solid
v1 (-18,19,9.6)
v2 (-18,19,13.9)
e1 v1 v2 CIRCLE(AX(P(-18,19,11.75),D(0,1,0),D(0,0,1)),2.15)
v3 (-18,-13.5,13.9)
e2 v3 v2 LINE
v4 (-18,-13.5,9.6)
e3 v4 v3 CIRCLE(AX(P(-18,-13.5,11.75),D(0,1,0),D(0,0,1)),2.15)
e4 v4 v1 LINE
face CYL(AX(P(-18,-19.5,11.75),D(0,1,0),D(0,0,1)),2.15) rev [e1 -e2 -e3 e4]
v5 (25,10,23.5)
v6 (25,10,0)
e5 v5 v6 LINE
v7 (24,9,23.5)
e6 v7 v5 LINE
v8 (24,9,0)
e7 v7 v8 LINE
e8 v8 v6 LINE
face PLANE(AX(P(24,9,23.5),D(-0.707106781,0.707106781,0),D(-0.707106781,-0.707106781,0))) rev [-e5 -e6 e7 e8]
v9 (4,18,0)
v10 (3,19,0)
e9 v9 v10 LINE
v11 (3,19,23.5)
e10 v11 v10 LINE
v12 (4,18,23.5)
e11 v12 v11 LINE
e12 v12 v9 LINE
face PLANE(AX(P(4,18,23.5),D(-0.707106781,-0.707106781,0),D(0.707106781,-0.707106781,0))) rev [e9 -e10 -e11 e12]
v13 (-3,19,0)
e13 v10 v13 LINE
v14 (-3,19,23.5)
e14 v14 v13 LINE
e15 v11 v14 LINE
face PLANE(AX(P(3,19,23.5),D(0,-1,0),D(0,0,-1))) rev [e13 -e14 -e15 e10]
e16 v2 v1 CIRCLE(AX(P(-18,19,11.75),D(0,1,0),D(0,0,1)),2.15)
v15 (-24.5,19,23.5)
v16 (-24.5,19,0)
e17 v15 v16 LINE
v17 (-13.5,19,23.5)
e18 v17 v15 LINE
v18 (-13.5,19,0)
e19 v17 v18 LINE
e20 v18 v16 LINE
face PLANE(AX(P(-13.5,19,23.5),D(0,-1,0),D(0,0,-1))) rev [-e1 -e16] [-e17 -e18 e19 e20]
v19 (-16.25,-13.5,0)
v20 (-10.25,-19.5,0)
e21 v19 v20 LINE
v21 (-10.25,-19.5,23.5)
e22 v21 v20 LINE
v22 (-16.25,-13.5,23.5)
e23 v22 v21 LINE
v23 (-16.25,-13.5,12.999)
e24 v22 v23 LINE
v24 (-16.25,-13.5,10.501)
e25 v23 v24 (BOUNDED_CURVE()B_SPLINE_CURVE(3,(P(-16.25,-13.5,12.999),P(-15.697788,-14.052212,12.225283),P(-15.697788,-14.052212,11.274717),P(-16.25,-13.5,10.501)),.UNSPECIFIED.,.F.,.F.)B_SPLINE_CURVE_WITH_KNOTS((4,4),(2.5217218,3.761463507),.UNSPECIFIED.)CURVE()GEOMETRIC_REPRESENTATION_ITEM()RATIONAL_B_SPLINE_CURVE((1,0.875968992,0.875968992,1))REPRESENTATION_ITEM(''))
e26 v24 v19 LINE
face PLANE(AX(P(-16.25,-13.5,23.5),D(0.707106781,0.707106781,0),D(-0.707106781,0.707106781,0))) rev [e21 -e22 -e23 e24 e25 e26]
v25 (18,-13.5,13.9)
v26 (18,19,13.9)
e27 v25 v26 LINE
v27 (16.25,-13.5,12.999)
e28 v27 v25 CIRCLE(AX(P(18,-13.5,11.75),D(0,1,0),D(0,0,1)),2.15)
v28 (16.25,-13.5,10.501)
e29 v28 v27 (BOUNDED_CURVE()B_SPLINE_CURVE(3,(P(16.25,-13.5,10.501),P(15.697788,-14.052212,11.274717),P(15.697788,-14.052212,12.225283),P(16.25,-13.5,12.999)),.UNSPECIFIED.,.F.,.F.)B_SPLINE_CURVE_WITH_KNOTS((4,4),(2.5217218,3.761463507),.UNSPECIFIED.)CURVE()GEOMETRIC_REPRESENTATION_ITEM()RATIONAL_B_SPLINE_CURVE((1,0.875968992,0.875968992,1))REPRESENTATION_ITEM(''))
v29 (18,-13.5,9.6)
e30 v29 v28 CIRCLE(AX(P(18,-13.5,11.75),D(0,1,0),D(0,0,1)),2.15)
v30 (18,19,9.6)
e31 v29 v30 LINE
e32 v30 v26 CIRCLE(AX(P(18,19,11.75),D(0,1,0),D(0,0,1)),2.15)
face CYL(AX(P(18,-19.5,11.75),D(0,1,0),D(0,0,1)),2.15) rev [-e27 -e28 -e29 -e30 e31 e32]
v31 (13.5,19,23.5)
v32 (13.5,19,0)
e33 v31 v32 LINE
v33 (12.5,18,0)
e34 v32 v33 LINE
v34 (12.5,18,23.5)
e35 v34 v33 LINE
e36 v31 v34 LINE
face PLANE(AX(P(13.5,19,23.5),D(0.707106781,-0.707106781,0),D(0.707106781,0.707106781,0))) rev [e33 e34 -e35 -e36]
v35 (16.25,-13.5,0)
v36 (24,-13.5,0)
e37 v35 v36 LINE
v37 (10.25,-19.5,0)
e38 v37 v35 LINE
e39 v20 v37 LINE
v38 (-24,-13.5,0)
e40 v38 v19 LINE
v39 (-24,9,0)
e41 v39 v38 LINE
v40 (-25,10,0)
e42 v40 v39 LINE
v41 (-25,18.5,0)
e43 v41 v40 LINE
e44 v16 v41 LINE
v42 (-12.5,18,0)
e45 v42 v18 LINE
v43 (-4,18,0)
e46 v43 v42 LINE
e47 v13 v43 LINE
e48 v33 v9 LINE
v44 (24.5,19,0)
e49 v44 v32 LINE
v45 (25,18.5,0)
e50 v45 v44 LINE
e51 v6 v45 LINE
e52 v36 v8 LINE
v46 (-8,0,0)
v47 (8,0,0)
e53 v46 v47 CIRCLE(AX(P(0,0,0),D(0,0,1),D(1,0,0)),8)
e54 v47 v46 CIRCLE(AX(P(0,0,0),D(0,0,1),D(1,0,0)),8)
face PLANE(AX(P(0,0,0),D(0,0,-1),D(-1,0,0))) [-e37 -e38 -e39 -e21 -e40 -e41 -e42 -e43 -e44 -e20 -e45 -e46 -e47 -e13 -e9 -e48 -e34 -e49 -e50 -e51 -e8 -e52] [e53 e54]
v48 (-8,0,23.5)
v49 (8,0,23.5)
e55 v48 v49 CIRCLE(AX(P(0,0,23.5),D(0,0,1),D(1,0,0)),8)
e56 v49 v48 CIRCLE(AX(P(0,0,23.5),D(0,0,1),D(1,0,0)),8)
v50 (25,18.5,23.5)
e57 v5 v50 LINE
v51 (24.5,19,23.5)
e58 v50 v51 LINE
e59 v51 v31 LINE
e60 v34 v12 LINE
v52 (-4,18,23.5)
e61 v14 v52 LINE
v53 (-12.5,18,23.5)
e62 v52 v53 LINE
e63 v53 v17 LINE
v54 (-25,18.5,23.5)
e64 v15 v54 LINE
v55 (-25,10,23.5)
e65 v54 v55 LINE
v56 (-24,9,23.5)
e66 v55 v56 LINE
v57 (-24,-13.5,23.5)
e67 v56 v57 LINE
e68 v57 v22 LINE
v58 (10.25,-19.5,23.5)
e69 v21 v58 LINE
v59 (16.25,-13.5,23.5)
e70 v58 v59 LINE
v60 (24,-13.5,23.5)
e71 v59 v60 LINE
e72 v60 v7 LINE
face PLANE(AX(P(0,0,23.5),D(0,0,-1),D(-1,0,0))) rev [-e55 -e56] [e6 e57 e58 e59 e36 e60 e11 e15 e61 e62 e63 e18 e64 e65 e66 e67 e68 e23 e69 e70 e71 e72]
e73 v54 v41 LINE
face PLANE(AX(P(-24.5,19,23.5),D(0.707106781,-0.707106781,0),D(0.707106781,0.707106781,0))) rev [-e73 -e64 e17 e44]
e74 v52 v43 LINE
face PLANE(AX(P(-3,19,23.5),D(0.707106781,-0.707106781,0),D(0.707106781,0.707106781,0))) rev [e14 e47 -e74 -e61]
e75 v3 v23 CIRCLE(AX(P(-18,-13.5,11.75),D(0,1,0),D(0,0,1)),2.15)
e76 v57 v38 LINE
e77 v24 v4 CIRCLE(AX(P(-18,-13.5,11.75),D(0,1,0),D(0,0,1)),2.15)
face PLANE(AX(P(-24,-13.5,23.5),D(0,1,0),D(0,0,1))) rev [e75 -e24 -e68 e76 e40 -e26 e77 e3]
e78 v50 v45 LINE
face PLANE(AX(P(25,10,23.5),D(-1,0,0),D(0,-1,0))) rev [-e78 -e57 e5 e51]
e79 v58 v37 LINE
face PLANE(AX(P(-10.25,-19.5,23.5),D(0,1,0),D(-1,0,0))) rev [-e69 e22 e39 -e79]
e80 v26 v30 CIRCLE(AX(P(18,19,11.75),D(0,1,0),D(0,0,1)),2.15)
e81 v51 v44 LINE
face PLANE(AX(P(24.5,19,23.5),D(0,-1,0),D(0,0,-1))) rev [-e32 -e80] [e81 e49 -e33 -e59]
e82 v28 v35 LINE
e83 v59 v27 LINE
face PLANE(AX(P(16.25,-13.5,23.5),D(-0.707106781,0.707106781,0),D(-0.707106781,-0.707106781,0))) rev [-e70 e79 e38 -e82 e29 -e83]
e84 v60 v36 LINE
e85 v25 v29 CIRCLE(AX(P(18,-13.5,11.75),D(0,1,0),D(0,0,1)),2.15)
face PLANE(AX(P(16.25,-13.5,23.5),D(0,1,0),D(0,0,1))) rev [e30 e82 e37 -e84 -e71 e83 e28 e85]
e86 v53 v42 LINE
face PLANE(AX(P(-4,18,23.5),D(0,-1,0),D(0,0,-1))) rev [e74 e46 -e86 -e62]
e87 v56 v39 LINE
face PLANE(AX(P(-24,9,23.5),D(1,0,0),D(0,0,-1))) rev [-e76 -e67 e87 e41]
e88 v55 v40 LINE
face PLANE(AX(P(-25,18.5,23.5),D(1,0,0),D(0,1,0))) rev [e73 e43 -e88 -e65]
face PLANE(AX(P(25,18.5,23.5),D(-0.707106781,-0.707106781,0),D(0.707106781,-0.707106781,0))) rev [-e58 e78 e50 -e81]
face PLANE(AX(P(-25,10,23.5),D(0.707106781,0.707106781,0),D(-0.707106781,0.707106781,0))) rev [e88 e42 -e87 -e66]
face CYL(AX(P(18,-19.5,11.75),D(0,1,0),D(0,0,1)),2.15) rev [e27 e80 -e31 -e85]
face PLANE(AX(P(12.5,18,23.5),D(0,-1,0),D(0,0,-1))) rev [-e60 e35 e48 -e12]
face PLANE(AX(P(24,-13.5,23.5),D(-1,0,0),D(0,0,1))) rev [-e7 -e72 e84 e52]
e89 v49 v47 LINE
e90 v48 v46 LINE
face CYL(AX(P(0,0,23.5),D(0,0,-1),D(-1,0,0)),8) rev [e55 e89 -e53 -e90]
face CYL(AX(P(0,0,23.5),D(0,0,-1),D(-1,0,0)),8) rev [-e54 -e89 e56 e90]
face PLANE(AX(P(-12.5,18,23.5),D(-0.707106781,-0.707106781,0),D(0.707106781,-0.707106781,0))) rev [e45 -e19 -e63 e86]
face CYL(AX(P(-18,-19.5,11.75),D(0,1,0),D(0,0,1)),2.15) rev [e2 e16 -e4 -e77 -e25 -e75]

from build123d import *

# Parameters (mm, degrees)
SKETCH_1_R          = 8
EXTRUDE_1_DEPTH     = 23.5
SKETCH_2_R          = 2.15
CUT_EXTRUDE_1_DEPTH = 52.570340313


with BuildPart() as part:
    # 草图1 → 凸台-拉伸1 (new body)
    with BuildSketch(Plane.XY):
        Polygon((-10.25, -19.5), (10.25, -19.5), (16.25, -13.5), (24, -13.5), (24, 9), (25, 10), (25, 18.5), (24.5, 19), (13.5, 19), (12.5, 18), (4, 18), (3, 19), (-3, 19), (-4, 18), (-12.5, 18), (-13.5, 19), (-24.5, 19), (-25, 18.5), (-25, 10), (-24, 9), (-24, -13.5), (-16.25, -13.5), align=None)
        Circle(SKETCH_1_R, mode=Mode.SUBTRACT)
    extrude(amount=EXTRUDE_1_DEPTH)

    # 草图2 → 切除-拉伸1 (cut, through all)
    with BuildSketch(Plane(origin=(0, 19, 0), x_dir=(1, 0, 0), z_dir=(0, 1, 0))):
        with Locations(Location((-18, -11.75, 0), (0, 0, 270))):
            Circle(SKETCH_2_R)
        with Locations(Location((18, -11.75, 0), (0, 0, 270))):
            Circle(SKETCH_2_R)
    extrude(amount=-CUT_EXTRUDE_1_DEPTH, mode=Mode.SUBTRACT)


solid = part.part
